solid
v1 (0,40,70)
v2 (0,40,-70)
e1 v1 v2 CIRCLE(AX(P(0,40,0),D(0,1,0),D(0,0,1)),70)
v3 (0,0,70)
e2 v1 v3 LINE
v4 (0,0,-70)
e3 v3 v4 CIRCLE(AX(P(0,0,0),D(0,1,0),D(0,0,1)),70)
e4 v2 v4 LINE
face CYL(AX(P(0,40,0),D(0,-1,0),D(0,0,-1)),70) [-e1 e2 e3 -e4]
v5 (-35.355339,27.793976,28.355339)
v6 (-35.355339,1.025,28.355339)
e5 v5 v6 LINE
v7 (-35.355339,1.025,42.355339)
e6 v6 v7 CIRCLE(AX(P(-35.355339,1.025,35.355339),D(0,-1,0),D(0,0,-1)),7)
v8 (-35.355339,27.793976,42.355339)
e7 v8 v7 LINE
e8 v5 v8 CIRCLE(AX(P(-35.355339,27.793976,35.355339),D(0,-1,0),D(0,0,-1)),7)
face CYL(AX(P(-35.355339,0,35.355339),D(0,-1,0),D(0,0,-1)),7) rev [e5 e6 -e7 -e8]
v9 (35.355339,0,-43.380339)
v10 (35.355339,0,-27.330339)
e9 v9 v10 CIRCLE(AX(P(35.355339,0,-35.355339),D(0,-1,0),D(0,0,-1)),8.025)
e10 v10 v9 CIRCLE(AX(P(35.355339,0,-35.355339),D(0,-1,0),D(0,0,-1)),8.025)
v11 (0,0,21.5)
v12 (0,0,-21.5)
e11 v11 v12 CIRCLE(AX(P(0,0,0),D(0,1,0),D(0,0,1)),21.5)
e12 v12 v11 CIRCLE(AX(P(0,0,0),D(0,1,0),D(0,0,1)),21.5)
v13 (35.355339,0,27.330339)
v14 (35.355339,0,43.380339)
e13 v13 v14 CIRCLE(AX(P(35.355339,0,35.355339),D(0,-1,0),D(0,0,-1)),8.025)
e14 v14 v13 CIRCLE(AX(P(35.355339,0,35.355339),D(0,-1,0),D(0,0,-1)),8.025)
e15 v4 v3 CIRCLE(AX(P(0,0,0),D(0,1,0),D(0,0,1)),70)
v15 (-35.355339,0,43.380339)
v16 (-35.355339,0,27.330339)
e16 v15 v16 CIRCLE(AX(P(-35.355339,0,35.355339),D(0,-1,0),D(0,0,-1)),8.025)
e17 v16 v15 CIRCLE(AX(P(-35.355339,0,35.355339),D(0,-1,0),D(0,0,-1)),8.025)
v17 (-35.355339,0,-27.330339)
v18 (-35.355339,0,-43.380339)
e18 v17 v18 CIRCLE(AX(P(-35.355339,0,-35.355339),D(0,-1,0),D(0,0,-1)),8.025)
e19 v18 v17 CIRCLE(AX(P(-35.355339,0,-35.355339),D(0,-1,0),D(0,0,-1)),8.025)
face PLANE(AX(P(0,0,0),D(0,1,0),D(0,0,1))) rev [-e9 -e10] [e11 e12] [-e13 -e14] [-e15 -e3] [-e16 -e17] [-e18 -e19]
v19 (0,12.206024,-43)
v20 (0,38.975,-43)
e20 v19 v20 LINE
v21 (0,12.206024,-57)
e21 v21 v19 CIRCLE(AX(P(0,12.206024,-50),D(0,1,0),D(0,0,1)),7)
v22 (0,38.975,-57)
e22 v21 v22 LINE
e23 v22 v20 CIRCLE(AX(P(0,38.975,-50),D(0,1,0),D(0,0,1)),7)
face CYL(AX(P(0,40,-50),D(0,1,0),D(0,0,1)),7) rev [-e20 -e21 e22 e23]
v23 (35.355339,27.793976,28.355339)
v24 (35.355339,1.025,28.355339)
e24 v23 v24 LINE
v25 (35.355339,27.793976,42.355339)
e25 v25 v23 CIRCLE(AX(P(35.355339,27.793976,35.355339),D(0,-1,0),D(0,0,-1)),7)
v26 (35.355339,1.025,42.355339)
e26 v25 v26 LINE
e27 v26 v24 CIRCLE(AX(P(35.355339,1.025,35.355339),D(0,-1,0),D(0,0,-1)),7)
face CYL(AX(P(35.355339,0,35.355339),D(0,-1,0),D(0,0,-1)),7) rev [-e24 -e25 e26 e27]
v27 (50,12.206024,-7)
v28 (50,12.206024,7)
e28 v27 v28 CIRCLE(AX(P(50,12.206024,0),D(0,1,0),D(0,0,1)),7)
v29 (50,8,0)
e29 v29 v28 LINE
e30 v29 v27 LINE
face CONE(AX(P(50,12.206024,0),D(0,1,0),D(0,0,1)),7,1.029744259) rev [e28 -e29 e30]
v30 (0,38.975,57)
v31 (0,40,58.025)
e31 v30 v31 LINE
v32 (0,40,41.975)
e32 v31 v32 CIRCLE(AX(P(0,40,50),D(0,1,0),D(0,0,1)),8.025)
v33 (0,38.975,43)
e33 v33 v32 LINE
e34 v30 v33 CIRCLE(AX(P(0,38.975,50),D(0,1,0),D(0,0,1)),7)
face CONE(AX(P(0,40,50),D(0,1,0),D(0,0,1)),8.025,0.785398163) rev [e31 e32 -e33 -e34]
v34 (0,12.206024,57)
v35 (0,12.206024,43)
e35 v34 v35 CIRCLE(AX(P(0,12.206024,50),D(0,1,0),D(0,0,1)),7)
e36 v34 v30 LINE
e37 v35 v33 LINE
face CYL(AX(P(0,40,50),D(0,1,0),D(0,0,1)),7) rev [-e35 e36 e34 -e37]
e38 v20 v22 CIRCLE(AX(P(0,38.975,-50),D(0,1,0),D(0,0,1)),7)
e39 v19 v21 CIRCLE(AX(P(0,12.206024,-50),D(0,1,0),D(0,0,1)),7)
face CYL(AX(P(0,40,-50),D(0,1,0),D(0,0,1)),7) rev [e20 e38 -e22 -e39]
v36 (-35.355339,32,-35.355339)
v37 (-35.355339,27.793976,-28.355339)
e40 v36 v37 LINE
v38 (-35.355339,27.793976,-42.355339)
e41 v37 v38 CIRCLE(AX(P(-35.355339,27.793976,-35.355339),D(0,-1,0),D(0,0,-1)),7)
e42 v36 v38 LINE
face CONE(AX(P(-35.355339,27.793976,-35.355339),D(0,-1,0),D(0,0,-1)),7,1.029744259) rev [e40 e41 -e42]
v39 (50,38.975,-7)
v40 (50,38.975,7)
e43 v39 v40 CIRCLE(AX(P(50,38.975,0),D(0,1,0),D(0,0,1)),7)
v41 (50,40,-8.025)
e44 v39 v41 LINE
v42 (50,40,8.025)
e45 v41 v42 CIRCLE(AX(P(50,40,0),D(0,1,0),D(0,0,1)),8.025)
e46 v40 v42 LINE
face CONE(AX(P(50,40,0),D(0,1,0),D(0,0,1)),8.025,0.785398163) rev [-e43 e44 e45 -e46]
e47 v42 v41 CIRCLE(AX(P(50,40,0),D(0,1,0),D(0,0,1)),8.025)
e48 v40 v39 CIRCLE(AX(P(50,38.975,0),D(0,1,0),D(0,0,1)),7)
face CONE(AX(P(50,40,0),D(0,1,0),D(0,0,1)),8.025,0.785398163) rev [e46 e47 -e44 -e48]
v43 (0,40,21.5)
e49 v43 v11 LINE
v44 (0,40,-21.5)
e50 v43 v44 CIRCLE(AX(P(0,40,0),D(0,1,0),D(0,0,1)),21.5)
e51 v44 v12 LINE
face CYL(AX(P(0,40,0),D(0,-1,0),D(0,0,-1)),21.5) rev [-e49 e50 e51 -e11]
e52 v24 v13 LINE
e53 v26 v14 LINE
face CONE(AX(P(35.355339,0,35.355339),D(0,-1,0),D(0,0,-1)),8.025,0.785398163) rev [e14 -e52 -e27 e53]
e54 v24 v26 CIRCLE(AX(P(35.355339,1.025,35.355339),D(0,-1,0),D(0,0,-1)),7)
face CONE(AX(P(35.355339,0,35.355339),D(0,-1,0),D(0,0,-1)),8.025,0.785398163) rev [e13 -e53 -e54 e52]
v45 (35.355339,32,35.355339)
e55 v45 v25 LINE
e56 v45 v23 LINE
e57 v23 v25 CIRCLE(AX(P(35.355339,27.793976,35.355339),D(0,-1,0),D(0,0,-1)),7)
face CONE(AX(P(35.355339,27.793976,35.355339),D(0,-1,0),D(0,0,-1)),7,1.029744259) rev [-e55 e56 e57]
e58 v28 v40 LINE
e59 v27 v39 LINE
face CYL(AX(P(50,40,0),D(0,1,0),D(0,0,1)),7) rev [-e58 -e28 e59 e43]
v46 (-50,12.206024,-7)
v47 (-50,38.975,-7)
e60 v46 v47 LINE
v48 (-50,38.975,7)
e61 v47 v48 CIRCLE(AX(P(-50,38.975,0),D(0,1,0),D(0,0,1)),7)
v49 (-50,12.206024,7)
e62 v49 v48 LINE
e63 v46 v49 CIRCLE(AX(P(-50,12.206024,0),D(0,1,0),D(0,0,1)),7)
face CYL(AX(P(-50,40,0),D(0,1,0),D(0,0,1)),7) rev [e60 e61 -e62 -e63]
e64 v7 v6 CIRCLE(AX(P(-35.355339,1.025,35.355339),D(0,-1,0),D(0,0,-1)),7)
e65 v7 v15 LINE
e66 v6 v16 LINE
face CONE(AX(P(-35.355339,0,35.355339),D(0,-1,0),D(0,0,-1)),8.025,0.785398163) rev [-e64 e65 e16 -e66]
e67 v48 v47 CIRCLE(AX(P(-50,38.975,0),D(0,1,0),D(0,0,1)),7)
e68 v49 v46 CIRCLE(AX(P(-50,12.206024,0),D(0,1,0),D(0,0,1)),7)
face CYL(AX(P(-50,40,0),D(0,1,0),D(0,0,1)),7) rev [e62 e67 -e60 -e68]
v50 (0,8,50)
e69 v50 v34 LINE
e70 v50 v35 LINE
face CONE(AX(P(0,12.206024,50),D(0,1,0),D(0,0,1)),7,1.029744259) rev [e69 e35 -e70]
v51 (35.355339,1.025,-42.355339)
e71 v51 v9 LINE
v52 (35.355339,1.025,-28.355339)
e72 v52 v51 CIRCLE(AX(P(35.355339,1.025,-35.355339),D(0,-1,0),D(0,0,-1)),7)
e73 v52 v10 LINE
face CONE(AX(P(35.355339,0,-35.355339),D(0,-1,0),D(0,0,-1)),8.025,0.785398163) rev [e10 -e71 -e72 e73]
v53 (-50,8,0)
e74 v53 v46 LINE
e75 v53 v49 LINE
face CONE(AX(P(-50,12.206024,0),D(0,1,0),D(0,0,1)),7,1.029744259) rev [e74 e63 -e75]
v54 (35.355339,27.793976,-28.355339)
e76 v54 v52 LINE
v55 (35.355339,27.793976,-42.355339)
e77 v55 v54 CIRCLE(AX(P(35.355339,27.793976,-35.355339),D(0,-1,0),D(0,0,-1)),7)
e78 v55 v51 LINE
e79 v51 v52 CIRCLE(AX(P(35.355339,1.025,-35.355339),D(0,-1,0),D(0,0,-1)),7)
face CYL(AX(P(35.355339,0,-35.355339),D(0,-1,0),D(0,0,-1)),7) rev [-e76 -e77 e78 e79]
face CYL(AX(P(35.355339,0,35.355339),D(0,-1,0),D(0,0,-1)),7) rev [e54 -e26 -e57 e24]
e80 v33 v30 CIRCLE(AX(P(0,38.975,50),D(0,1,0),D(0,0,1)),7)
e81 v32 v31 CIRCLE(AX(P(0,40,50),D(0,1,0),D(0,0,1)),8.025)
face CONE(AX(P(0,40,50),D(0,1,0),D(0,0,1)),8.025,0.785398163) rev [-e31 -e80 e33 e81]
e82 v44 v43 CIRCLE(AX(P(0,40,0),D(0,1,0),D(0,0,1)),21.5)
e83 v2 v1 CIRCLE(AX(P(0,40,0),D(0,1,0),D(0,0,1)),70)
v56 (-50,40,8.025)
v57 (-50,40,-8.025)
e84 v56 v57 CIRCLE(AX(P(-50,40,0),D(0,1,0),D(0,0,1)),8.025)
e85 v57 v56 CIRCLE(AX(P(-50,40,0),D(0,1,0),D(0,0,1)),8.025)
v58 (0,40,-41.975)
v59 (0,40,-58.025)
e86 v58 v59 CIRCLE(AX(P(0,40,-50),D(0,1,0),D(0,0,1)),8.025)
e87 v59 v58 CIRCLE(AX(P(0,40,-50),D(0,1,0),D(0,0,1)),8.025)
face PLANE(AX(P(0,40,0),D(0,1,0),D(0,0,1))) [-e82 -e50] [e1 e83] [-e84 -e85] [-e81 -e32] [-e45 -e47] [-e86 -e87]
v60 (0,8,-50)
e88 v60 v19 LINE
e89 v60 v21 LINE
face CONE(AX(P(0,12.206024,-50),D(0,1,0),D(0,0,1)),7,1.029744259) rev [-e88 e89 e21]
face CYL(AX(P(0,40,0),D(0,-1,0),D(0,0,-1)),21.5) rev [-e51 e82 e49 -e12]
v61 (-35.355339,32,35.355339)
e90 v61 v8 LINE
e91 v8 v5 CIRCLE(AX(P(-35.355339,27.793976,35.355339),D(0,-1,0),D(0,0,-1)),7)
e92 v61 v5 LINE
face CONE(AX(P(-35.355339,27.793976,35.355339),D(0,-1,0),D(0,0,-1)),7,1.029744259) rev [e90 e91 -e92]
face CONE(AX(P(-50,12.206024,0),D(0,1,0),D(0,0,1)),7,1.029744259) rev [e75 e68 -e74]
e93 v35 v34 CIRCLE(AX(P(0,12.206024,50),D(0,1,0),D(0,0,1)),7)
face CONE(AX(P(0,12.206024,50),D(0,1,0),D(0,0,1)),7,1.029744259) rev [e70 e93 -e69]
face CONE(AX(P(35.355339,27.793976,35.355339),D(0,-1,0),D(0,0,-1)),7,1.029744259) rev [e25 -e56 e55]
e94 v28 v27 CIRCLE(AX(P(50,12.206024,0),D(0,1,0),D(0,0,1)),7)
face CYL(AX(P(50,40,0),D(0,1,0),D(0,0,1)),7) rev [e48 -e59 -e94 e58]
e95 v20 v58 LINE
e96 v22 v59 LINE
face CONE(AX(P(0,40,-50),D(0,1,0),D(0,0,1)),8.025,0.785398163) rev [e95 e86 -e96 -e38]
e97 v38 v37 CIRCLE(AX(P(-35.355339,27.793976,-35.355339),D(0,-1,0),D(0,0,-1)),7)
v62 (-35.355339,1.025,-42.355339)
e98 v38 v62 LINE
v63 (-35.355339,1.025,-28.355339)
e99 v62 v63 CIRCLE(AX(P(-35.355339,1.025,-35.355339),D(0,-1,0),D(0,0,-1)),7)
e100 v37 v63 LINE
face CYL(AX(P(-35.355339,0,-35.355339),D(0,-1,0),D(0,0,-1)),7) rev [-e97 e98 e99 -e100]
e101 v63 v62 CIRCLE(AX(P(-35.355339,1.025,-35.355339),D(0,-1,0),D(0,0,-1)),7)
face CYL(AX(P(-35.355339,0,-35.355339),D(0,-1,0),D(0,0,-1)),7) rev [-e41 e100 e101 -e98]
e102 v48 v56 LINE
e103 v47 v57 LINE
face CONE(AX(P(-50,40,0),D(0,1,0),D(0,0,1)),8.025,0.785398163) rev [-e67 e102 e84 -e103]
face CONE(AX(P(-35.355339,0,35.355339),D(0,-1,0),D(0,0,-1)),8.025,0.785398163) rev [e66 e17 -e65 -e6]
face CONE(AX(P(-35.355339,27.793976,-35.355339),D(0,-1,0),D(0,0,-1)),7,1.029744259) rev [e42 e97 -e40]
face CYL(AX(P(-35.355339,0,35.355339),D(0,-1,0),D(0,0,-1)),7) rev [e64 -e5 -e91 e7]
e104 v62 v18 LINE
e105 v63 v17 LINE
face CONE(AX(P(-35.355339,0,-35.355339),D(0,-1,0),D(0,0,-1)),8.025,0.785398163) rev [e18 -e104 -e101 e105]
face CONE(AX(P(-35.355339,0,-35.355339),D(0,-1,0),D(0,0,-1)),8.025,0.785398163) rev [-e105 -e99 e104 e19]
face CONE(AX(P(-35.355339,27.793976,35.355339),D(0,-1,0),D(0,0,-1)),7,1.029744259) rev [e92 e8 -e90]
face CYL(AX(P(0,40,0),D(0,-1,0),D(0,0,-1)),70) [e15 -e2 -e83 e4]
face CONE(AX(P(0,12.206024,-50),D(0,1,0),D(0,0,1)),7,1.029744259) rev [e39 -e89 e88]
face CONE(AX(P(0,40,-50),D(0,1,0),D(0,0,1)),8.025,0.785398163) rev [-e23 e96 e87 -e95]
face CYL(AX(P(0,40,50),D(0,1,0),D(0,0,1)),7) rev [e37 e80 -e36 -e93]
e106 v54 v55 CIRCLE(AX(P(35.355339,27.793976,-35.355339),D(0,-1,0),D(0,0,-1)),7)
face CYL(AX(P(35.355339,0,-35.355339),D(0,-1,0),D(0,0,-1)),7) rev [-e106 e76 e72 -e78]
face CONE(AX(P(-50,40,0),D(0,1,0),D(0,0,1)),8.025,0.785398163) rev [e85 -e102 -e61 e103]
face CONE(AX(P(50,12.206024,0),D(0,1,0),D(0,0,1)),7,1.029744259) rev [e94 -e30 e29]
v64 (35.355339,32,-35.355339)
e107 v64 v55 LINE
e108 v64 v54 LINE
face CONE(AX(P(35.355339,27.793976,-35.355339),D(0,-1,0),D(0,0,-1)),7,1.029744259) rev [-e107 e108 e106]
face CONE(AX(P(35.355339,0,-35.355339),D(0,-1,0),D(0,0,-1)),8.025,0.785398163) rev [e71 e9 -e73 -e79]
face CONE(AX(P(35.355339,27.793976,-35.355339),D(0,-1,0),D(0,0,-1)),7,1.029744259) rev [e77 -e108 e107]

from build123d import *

# Parameters (mm, degrees)
SKETCH_1_R                    = 70
SKETCH_1_R_2                  = 21.5
EXTRUDE_1_DEPTH               = 40
HOLE_WIZARD_M16_1_D           = 14
HOLE_WIZARD_M16_1_DEPTH       = 27.793975667
HOLE_WIZARD_M16_1_CSINK_D     = 16.05
HOLE_WIZARD_M16_1_CSINK_ANGLE = 90
HOLE_WIZARD_M16_1_TIP         = 4.206024333
HOLE_WIZARD_M16_3_D           = 14
HOLE_WIZARD_M16_3_DEPTH       = 27.793975667
HOLE_WIZARD_M16_3_CSINK_D     = 16.05
HOLE_WIZARD_M16_3_CSINK_ANGLE = 90
HOLE_WIZARD_M16_3_TIP         = 4.206024333


with BuildPart() as part:
    # 草图1 → 凸台-拉伸1 (new body)
    with BuildSketch(Plane(origin=(0, 0, 0), x_dir=(1, 0, 0), z_dir=(0, 1, 0))):
        with Locations(Location((0, 0, 0), (0, 0, 270))):
            Circle(SKETCH_1_R)
        with Locations(Location((0, 0, 0), (0, 0, 270))):
            Circle(SKETCH_1_R_2, mode=Mode.SUBTRACT)
    extrude(amount=EXTRUDE_1_DEPTH)

    # M16 螺纹孔1
    with Locations(Plane(origin=(0, 40, 0), x_dir=(1, 0, 0), z_dir=(0, 1, 0))):
        with Locations((0, 50), (50, 0), (0, -50), (-50, 0)):
            CounterSinkHole(HOLE_WIZARD_M16_1_D / 2, HOLE_WIZARD_M16_1_CSINK_D / 2, depth=HOLE_WIZARD_M16_1_DEPTH, counter_sink_angle=HOLE_WIZARD_M16_1_CSINK_ANGLE)
            with Locations((0, 0, -(HOLE_WIZARD_M16_1_DEPTH + HOLE_WIZARD_M16_1_TIP / 2))):  # 118° drill point
                Cone(0, HOLE_WIZARD_M16_1_D / 2, HOLE_WIZARD_M16_1_TIP, mode=Mode.SUBTRACT)

    # M16 螺纹孔3
    with Locations(Plane(origin=(0, 0, 0), x_dir=(-1, 0, 0), z_dir=(0, -1, 0))):
        with Locations((-35.355339059, 35.355339059), (35.355339059, 35.355339059), (35.355339059, -35.355339059), (-35.355339059, -35.355339059)):
            CounterSinkHole(HOLE_WIZARD_M16_3_D / 2, HOLE_WIZARD_M16_3_CSINK_D / 2, depth=HOLE_WIZARD_M16_3_DEPTH, counter_sink_angle=HOLE_WIZARD_M16_3_CSINK_ANGLE)
            with Locations((0, 0, -(HOLE_WIZARD_M16_3_DEPTH + HOLE_WIZARD_M16_3_TIP / 2))):  # 118° drill point
                Cone(0, HOLE_WIZARD_M16_3_D / 2, HOLE_WIZARD_M16_3_TIP, mode=Mode.SUBTRACT)


solid = part.part
